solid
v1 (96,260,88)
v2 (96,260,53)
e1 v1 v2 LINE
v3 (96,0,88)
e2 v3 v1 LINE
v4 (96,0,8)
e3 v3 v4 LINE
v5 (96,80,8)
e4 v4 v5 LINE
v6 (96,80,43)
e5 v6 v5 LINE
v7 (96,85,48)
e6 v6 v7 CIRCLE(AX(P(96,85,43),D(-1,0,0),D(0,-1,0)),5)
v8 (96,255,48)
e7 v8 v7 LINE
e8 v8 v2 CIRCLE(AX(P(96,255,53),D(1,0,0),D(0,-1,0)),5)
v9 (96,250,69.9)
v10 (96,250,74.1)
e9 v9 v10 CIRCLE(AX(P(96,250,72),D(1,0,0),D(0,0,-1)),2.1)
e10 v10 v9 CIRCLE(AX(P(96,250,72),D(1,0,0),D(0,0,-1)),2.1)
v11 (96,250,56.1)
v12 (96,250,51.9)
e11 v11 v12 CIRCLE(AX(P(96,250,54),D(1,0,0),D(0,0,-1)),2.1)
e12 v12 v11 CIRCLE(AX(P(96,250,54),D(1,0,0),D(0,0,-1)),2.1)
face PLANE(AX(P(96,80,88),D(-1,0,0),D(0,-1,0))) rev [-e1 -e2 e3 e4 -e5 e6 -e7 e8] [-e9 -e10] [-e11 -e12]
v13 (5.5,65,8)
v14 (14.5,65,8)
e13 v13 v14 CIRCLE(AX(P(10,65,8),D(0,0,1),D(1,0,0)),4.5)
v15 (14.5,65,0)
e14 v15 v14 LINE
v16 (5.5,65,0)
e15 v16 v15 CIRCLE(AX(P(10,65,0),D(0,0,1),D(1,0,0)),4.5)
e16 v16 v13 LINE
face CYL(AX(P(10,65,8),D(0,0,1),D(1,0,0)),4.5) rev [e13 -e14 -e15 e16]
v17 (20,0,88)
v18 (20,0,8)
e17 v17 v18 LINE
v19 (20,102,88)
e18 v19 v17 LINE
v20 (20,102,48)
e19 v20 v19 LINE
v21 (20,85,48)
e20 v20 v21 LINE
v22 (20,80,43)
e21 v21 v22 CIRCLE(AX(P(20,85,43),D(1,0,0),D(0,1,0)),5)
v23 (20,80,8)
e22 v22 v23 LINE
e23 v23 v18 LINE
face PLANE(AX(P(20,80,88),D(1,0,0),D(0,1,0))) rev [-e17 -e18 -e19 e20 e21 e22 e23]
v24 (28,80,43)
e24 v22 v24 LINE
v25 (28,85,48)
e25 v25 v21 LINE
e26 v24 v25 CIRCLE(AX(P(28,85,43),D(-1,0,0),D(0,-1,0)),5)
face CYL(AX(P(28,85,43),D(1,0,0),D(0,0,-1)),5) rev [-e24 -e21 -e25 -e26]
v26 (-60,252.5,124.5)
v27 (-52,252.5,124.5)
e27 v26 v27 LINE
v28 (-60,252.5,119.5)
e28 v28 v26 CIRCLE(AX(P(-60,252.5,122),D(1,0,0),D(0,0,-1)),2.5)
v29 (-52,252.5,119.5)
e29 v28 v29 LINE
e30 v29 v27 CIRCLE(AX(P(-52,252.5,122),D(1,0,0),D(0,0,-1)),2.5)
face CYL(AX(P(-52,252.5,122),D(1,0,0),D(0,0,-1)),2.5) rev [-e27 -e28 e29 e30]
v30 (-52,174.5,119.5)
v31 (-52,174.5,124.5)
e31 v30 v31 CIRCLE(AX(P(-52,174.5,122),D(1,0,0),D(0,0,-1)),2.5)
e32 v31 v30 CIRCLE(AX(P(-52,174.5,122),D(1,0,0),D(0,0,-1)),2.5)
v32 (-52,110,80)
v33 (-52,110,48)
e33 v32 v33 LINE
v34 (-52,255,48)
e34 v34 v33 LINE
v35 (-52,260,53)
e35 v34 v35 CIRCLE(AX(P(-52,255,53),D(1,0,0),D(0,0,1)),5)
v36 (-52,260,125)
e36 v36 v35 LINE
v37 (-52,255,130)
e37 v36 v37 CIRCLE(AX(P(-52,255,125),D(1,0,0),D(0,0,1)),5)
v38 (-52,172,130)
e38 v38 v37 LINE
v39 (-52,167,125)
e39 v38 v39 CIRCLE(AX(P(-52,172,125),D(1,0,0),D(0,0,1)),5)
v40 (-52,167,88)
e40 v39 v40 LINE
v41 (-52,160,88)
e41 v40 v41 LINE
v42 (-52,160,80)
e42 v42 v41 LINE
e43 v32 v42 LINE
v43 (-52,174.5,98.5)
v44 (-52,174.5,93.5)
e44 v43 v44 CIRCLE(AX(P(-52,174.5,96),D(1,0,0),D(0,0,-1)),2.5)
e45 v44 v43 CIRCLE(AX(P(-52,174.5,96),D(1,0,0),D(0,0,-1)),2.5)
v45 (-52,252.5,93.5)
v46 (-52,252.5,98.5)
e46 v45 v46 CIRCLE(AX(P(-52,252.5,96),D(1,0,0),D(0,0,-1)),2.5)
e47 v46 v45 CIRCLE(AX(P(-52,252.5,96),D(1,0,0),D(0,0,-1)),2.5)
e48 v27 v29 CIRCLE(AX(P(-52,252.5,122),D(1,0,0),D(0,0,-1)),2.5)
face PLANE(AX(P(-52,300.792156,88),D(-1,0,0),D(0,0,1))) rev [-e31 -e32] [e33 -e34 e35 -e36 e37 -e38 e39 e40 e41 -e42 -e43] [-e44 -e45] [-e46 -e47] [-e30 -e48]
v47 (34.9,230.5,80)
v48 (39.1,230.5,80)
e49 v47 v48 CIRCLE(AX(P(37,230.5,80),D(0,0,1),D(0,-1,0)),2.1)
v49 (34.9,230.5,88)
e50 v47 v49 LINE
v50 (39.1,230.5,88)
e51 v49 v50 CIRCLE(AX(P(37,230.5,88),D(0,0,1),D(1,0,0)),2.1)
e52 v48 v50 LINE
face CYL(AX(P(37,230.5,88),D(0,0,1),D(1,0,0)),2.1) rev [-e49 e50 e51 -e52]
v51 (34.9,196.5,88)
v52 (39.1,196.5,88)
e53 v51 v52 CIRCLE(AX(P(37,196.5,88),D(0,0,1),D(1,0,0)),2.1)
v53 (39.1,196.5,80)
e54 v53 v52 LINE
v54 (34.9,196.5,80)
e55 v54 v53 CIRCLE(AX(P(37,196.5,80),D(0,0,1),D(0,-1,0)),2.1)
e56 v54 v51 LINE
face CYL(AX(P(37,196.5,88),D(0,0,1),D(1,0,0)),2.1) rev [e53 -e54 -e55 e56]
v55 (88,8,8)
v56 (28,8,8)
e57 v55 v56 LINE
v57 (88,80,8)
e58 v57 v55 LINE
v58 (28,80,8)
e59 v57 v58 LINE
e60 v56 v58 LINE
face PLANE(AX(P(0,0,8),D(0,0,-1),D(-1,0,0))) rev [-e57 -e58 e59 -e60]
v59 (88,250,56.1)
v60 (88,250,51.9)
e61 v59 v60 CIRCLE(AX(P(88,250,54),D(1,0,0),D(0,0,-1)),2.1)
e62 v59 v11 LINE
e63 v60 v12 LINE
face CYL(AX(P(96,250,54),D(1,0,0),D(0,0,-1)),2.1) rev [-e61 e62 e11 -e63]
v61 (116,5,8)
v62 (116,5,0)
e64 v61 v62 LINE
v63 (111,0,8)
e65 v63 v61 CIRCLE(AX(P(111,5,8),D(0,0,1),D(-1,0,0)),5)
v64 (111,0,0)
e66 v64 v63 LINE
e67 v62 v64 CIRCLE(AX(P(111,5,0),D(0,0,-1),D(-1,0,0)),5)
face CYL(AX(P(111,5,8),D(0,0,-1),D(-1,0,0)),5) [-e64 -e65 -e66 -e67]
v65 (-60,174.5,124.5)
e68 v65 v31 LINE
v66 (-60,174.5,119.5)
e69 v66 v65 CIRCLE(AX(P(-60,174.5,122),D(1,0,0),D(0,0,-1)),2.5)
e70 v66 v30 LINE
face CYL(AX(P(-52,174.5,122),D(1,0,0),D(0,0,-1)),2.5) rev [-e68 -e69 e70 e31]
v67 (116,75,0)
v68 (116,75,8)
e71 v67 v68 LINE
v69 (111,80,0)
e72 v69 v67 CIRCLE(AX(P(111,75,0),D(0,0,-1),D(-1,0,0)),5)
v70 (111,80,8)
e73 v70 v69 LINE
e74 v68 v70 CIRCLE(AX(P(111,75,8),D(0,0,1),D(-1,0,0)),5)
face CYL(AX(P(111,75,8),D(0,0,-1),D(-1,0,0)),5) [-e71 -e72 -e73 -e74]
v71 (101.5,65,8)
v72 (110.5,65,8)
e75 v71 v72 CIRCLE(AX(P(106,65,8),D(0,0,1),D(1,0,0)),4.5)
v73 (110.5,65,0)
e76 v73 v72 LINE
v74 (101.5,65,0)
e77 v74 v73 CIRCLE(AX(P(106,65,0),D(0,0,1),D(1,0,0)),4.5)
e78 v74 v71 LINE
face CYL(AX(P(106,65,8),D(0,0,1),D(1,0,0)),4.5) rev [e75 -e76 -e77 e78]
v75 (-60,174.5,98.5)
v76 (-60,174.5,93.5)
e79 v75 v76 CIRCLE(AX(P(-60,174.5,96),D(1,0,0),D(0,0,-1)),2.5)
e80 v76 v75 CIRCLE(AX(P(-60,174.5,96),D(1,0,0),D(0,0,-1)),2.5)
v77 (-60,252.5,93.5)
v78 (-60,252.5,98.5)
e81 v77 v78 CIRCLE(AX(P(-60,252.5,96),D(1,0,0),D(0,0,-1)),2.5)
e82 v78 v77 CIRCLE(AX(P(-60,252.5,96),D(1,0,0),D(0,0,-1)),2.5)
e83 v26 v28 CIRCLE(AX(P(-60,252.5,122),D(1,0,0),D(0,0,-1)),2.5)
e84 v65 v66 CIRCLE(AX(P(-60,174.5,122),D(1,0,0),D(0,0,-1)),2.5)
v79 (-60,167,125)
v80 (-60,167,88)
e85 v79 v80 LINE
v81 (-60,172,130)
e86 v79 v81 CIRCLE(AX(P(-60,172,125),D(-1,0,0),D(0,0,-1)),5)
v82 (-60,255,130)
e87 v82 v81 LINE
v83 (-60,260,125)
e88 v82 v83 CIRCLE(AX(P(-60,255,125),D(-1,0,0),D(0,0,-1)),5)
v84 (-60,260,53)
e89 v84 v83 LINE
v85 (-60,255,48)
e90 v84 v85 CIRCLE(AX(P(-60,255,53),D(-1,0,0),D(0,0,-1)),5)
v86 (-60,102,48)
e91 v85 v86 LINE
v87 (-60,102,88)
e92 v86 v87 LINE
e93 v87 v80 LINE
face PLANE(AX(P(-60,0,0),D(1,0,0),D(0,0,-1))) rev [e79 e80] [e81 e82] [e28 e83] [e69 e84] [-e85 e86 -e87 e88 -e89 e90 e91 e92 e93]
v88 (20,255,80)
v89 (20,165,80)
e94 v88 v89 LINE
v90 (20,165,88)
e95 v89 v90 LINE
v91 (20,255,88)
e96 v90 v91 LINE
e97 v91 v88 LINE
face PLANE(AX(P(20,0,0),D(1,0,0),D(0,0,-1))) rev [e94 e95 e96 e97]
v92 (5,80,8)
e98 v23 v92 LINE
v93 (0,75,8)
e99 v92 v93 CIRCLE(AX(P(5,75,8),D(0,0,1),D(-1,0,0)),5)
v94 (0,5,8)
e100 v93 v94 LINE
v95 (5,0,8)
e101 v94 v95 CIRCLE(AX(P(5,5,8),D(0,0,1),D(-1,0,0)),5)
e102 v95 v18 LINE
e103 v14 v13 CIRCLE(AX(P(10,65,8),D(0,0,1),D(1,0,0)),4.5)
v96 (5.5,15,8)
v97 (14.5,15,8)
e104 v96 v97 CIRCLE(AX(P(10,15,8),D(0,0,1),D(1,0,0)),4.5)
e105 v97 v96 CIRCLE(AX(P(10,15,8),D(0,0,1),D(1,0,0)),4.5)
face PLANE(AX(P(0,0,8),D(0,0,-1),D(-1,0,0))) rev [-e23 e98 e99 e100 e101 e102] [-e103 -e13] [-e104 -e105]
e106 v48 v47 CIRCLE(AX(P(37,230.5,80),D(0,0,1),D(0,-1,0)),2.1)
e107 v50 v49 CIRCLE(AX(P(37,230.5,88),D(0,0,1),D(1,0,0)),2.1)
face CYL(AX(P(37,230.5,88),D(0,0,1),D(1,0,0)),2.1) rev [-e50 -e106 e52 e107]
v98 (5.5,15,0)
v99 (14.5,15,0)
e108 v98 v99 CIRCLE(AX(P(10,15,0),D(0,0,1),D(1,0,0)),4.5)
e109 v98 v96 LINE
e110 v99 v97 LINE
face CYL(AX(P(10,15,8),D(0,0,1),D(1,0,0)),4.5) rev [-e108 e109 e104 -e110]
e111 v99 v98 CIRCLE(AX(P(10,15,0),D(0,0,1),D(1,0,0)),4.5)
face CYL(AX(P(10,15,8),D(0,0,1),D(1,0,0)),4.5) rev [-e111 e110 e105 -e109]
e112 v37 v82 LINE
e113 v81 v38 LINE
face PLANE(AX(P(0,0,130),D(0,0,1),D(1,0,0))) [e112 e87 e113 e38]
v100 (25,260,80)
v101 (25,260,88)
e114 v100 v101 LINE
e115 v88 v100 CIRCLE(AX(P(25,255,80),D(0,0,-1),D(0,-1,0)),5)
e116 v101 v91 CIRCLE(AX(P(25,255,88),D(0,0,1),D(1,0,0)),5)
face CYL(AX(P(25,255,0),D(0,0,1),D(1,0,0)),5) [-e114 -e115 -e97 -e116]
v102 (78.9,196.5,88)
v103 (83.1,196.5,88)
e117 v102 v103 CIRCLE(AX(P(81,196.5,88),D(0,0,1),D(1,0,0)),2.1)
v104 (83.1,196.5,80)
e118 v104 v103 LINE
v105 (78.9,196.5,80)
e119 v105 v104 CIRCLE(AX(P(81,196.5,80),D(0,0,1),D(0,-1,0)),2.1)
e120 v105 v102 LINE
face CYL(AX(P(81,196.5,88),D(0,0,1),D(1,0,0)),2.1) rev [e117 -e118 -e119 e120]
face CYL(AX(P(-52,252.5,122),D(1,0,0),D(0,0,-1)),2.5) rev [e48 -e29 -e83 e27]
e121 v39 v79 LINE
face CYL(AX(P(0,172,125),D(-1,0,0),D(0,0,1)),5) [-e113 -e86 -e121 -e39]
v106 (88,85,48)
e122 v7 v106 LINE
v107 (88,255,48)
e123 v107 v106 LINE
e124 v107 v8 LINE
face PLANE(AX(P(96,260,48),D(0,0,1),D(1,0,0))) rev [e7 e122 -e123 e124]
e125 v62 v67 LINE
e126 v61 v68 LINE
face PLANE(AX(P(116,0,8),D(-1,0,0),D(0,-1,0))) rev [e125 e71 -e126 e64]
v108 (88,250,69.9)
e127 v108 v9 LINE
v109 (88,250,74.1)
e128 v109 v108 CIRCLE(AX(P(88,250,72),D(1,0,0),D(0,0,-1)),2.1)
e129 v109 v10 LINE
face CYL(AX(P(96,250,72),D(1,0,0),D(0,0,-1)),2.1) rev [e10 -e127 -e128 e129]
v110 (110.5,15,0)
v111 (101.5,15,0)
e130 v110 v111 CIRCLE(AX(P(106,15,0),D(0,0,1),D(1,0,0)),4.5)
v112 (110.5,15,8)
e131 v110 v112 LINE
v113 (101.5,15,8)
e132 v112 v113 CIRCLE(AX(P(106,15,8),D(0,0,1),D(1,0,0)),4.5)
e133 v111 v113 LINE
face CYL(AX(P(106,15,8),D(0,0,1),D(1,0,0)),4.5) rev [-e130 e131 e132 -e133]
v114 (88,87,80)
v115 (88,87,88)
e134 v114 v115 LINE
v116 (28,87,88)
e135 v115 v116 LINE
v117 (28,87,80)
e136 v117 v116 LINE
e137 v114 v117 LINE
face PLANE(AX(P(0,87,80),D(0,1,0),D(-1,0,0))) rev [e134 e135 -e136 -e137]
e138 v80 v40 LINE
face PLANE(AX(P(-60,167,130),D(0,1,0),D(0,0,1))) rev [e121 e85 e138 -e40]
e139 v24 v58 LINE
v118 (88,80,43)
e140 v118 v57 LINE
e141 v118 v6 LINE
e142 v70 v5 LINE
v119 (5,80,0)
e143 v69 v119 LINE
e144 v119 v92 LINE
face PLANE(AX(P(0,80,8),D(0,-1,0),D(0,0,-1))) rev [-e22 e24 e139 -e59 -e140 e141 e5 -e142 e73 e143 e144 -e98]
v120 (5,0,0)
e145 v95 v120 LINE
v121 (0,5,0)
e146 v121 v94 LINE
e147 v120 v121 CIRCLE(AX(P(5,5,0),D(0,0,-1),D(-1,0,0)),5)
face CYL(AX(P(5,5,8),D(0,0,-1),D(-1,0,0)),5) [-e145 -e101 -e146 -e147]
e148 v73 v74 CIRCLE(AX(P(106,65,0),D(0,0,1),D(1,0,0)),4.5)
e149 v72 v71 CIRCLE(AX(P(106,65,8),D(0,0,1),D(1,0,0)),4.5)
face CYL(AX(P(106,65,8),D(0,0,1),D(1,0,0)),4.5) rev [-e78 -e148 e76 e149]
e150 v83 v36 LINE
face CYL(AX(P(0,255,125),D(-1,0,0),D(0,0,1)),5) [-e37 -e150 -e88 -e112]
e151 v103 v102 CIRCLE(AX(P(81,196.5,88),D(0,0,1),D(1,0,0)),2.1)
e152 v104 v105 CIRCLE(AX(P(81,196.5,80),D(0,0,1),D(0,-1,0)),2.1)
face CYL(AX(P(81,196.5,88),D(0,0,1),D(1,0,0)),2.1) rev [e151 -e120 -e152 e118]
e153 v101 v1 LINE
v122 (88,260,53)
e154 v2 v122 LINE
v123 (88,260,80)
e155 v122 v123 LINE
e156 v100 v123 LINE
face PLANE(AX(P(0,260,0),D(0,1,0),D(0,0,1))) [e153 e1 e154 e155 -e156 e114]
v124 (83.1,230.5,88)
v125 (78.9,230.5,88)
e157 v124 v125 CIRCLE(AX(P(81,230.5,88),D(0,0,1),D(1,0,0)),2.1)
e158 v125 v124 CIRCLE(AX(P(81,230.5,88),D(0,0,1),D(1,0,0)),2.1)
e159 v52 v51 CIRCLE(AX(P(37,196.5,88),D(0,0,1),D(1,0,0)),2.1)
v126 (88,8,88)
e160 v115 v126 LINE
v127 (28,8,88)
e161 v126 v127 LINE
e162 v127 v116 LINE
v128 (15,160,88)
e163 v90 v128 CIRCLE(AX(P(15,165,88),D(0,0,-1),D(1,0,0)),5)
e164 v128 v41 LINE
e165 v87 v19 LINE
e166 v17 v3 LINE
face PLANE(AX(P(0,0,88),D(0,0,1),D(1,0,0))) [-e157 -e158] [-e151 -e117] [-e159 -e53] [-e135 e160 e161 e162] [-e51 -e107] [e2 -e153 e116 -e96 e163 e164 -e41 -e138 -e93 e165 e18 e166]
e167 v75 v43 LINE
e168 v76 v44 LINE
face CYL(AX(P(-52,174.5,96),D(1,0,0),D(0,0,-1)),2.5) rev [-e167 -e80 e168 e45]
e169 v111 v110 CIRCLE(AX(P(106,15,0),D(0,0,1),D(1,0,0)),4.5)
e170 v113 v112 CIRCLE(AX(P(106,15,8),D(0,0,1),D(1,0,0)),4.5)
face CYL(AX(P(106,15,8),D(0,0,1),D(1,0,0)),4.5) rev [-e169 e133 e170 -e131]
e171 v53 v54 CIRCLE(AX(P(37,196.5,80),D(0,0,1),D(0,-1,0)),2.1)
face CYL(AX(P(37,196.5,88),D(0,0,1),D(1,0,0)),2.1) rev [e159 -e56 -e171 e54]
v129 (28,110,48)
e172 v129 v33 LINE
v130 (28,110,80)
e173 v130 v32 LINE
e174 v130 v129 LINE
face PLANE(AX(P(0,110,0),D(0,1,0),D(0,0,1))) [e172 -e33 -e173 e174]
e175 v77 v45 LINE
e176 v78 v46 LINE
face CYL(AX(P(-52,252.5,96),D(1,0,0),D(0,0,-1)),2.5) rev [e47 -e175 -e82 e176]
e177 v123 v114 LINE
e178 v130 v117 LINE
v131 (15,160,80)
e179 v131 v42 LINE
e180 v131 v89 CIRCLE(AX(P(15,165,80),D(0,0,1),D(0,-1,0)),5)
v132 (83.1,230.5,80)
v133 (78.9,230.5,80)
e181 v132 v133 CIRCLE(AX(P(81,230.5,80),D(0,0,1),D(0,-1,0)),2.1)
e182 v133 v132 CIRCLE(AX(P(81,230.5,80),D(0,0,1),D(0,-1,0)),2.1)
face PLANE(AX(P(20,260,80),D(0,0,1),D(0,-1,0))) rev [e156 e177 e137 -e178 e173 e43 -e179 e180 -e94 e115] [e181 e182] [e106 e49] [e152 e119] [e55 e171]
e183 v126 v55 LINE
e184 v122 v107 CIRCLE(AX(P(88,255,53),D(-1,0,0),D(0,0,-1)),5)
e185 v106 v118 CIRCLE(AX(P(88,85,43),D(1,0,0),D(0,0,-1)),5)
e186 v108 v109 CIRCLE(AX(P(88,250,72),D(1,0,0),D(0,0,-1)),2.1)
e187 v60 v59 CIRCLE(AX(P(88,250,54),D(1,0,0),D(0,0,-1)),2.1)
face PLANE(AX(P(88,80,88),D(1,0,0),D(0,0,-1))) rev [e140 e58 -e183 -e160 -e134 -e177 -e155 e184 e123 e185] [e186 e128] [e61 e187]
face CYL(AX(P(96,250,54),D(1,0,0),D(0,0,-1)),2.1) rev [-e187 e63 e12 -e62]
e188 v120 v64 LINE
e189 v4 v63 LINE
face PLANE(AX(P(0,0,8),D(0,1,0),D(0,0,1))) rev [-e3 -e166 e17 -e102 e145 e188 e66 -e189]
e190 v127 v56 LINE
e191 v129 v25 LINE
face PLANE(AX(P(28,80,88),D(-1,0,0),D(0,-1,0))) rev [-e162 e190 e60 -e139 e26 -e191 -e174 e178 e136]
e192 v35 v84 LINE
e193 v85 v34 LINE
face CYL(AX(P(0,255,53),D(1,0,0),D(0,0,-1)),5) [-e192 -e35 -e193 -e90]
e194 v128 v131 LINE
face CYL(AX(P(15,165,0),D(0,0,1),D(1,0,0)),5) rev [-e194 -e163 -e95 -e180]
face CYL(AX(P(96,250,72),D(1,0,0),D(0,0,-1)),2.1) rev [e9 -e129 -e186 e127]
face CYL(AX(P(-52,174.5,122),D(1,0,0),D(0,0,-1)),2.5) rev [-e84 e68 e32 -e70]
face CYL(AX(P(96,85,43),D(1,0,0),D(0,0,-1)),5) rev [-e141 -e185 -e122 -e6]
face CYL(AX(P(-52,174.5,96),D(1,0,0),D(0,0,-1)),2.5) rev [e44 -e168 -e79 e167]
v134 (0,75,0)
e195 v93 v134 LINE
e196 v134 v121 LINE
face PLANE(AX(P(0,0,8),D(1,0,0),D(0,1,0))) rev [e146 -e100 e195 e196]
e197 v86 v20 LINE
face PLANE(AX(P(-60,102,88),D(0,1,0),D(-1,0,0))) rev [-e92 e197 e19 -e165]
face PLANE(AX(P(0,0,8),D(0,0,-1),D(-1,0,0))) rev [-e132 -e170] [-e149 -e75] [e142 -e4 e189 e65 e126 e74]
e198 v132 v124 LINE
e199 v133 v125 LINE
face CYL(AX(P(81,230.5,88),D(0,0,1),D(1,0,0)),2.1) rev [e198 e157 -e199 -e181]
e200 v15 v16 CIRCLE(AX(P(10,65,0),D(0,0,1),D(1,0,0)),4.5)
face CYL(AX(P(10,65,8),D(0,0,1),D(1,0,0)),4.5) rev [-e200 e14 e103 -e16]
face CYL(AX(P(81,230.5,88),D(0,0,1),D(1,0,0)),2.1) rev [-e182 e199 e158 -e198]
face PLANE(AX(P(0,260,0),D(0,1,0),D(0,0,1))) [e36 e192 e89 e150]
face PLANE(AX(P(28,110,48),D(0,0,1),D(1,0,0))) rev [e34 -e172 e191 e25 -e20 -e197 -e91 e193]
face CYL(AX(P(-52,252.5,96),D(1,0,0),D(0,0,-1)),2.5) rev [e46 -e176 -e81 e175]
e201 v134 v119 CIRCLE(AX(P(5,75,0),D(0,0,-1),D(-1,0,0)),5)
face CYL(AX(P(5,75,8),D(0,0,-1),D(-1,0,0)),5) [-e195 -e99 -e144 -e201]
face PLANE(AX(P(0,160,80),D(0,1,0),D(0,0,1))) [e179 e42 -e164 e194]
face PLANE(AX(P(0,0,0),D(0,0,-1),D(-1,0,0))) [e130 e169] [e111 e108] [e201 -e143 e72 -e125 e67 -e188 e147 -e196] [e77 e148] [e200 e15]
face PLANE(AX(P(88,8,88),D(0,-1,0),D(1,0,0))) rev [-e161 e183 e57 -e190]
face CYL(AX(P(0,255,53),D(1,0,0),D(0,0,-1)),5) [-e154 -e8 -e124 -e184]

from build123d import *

# Parameters (mm, degrees)
SKETCH_1_W             = 116
SKETCH_1_H             = 80
EXTRUDE_1_DEPTH        = 8
SKETCH_2_W             = 8
SKETCH_2_H             = 80
EXTRUDE_2_DEPTH        = 80
SKETCH_4_W             = 8
SKETCH_4_H             = 40
EXTRUDE_3_DEPTH        = 180
SKETCH_5_W             = 60
SKETCH_5_H             = 8
EXTRUDE_4_DEPTH        = 80
SKETCH_8_W             = 8
SKETCH_8_H             = 40
EXTRUDE_7_DEPTH        = 30
SKETCH_10_W            = 40
SKETCH_10_H            = 8
EXTRUDE_8_DEPTH        = 80
SKETCH_11_W            = 8
SKETCH_11_H            = 40
EXTRUDE_9_DEPTH        = 150
SKETCH_12_W            = 8
SKETCH_12_H            = 93
EXTRUDE_10_DEPTH       = 68
SKETCH_14_W            = 8
SKETCH_14_H            = 93
EXTRUDE_12_DEPTH       = 42
FILLET_1_R             = 5
FILLET_2_R             = 5
HOLE_WIZARD_9_0_9_1_D  = 9
HOLE_WIZARD_M5_1_D     = 4.2
HOLE_WIZARD_M6_1_D     = 5
HOLE_WIZARD_M5_2_D     = 4.2
HOLE_WIZARD_M5_2_DEPTH = 10.4
HOLE_WIZARD_M5_2_TIP   = 1.2618073
EXTRUDE_15_DEPTH       = 8
FILLET_3_R             = 5


with BuildPart() as part:
    # 草图1 → 凸台-拉伸1 (new body)
    with BuildSketch(Plane.XY):
        with Locations((58, 40)):
            Rectangle(SKETCH_1_W, SKETCH_1_H)
    extrude(amount=EXTRUDE_1_DEPTH)

    # 草图2 → 凸台-拉伸2 (add)
    with BuildSketch(Plane.XY.offset(8)):
        with Locations((24, 40)):
            Rectangle(SKETCH_2_W, SKETCH_2_H)
        with Locations((92, 40)):
            Rectangle(SKETCH_2_W, SKETCH_2_H)
    extrude(amount=EXTRUDE_2_DEPTH)

    # 草图4 → 凸台-拉伸3 (add)
    with BuildSketch(Plane(origin=(0, 80, 0), x_dir=(1, 0, 0), z_dir=(0, 1, 0))):
        with Locations((92, -68)):
            Rectangle(SKETCH_4_W, SKETCH_4_H)
    extrude(amount=EXTRUDE_3_DEPTH)

    # 草图5 → 凸台-拉伸4 (add)
    with BuildSketch(Plane.XY.offset(8)):
        with Locations((58, 4)):
            Rectangle(SKETCH_5_W, SKETCH_5_H)
    extrude(amount=EXTRUDE_4_DEPTH)

    # 草图8 → 凸台-拉伸7 (add)
    with BuildSketch(Plane(origin=(0, 80, 0), x_dir=(1, 0, 0), z_dir=(0, 1, 0))):
        with Locations((24, -68)):
            Rectangle(SKETCH_8_W, SKETCH_8_H)
    extrude(amount=EXTRUDE_7_DEPTH)

    # 草图10 → 凸台-拉伸8 (add)
    with BuildSketch(Plane.ZY.offset(-20)):
        with Locations((68, 106)):
            Rectangle(SKETCH_10_W, SKETCH_10_H)
    extrude(amount=EXTRUDE_8_DEPTH)

    # 草图11 → 凸台-拉伸9 (add)
    with BuildSketch(Plane(origin=(0, 110, 0), x_dir=(1, 0, 0), z_dir=(0, 1, 0))):
        with Locations((-56, -68)):
            Rectangle(SKETCH_11_W, SKETCH_11_H)
    extrude(amount=EXTRUDE_9_DEPTH)

    # 草图12 → 凸台-拉伸10 (add)
    with BuildSketch(Plane.ZY.offset(-88)):
        with Locations((84, 213.5)):
            Rectangle(SKETCH_12_W, SKETCH_12_H)
    extrude(amount=EXTRUDE_10_DEPTH)

    # 草图14 → 凸台-拉伸12 (add)
    with BuildSketch(Plane.XY.offset(88)):
        with Locations((-56, 213.5)):
            Rectangle(SKETCH_14_W, SKETCH_14_H)
    extrude(amount=EXTRUDE_12_DEPTH)

    # 圆角1
    fillet_1_edges = [part.edges().sort_by_distance(p)[0] for p in [
        (-56, 260, 48),
        (24, 80, 48),
        (92, 80, 48),
        (92, 260, 48),
        (-56, 260, 130),
        (-56, 167, 130),
        (20, 260, 84),
    ]]
    fillet(fillet_1_edges, radius=FILLET_1_R)

    # 圆角2
    fillet_2_edges = [part.edges().sort_by_distance(p)[0] for p in [
        (0, 80, 4),
        (0, 0, 4),
        (116, 80, 4),
        (116, 0, 4),
    ]]
    fillet(fillet_2_edges, radius=FILLET_2_R)

    # Ø9.0 (9) 直径孔1 (through all)
    with Locations(Plane.XY.offset(8)):
        with Locations((106, 15), (106, 65)):
            hole_wizard_9_0_9_1 = Hole(HOLE_WIZARD_9_0_9_1_D / 2)

    # 镜向1: Ø9.0 (9) 直径孔1 across plane
    add(hole_wizard_9_0_9_1.mirror(Plane(origin=(58, 0, 0), x_dir=(0, 0, 1), z_dir=(1, 0, 0))), mode=Mode.SUBTRACT)

    # M5 螺纹孔1 (through all)
    with Locations(Plane.XY.offset(88)):
        with Locations((37, 196.5), (81, 196.5), (81, 230.5), (37, 230.5)):
            Hole(HOLE_WIZARD_M5_1_D / 2)

    # M6 螺纹孔1 (through all)
    with Locations(Plane(origin=(-52, 0, 0), x_dir=(0, 0, -1), z_dir=(1, 0, 0))):
        with Locations((-96, 252.5), (-122, 252.5), (-122, 174.5), (-96, 174.5)):
            Hole(HOLE_WIZARD_M6_1_D / 2)

    # M5 螺纹孔2
    with Locations(Plane(origin=(96, 0, 0), x_dir=(0, 0, -1), z_dir=(1, 0, 0))):
        with Locations((-72, 250), (-54, 250)):
            Hole(HOLE_WIZARD_M5_2_D / 2, depth=HOLE_WIZARD_M5_2_DEPTH)
            with Locations((0, 0, -(HOLE_WIZARD_M5_2_DEPTH + HOLE_WIZARD_M5_2_TIP / 2))):  # 118° drill point
                Cone(0, HOLE_WIZARD_M5_2_D / 2, HOLE_WIZARD_M5_2_TIP, mode=Mode.SUBTRACT)

    # 草图27 → 凸台-拉伸15 (add)
    with BuildSketch(Plane.XY.offset(88)):
        Polygon((88, 87), (88, 167), (20, 167), (20, 160), (-52, 160), (-52, 110), (28, 110), (28, 87), align=None)
    extrude(amount=-EXTRUDE_15_DEPTH)

    # 圆角3
    fillet_3_edges = [part.edges().sort_by_distance(p)[0] for p in [
        (20, 160, 84),
    ]]
    fillet(fillet_3_edges, radius=FILLET_3_R)


solid = part.part
